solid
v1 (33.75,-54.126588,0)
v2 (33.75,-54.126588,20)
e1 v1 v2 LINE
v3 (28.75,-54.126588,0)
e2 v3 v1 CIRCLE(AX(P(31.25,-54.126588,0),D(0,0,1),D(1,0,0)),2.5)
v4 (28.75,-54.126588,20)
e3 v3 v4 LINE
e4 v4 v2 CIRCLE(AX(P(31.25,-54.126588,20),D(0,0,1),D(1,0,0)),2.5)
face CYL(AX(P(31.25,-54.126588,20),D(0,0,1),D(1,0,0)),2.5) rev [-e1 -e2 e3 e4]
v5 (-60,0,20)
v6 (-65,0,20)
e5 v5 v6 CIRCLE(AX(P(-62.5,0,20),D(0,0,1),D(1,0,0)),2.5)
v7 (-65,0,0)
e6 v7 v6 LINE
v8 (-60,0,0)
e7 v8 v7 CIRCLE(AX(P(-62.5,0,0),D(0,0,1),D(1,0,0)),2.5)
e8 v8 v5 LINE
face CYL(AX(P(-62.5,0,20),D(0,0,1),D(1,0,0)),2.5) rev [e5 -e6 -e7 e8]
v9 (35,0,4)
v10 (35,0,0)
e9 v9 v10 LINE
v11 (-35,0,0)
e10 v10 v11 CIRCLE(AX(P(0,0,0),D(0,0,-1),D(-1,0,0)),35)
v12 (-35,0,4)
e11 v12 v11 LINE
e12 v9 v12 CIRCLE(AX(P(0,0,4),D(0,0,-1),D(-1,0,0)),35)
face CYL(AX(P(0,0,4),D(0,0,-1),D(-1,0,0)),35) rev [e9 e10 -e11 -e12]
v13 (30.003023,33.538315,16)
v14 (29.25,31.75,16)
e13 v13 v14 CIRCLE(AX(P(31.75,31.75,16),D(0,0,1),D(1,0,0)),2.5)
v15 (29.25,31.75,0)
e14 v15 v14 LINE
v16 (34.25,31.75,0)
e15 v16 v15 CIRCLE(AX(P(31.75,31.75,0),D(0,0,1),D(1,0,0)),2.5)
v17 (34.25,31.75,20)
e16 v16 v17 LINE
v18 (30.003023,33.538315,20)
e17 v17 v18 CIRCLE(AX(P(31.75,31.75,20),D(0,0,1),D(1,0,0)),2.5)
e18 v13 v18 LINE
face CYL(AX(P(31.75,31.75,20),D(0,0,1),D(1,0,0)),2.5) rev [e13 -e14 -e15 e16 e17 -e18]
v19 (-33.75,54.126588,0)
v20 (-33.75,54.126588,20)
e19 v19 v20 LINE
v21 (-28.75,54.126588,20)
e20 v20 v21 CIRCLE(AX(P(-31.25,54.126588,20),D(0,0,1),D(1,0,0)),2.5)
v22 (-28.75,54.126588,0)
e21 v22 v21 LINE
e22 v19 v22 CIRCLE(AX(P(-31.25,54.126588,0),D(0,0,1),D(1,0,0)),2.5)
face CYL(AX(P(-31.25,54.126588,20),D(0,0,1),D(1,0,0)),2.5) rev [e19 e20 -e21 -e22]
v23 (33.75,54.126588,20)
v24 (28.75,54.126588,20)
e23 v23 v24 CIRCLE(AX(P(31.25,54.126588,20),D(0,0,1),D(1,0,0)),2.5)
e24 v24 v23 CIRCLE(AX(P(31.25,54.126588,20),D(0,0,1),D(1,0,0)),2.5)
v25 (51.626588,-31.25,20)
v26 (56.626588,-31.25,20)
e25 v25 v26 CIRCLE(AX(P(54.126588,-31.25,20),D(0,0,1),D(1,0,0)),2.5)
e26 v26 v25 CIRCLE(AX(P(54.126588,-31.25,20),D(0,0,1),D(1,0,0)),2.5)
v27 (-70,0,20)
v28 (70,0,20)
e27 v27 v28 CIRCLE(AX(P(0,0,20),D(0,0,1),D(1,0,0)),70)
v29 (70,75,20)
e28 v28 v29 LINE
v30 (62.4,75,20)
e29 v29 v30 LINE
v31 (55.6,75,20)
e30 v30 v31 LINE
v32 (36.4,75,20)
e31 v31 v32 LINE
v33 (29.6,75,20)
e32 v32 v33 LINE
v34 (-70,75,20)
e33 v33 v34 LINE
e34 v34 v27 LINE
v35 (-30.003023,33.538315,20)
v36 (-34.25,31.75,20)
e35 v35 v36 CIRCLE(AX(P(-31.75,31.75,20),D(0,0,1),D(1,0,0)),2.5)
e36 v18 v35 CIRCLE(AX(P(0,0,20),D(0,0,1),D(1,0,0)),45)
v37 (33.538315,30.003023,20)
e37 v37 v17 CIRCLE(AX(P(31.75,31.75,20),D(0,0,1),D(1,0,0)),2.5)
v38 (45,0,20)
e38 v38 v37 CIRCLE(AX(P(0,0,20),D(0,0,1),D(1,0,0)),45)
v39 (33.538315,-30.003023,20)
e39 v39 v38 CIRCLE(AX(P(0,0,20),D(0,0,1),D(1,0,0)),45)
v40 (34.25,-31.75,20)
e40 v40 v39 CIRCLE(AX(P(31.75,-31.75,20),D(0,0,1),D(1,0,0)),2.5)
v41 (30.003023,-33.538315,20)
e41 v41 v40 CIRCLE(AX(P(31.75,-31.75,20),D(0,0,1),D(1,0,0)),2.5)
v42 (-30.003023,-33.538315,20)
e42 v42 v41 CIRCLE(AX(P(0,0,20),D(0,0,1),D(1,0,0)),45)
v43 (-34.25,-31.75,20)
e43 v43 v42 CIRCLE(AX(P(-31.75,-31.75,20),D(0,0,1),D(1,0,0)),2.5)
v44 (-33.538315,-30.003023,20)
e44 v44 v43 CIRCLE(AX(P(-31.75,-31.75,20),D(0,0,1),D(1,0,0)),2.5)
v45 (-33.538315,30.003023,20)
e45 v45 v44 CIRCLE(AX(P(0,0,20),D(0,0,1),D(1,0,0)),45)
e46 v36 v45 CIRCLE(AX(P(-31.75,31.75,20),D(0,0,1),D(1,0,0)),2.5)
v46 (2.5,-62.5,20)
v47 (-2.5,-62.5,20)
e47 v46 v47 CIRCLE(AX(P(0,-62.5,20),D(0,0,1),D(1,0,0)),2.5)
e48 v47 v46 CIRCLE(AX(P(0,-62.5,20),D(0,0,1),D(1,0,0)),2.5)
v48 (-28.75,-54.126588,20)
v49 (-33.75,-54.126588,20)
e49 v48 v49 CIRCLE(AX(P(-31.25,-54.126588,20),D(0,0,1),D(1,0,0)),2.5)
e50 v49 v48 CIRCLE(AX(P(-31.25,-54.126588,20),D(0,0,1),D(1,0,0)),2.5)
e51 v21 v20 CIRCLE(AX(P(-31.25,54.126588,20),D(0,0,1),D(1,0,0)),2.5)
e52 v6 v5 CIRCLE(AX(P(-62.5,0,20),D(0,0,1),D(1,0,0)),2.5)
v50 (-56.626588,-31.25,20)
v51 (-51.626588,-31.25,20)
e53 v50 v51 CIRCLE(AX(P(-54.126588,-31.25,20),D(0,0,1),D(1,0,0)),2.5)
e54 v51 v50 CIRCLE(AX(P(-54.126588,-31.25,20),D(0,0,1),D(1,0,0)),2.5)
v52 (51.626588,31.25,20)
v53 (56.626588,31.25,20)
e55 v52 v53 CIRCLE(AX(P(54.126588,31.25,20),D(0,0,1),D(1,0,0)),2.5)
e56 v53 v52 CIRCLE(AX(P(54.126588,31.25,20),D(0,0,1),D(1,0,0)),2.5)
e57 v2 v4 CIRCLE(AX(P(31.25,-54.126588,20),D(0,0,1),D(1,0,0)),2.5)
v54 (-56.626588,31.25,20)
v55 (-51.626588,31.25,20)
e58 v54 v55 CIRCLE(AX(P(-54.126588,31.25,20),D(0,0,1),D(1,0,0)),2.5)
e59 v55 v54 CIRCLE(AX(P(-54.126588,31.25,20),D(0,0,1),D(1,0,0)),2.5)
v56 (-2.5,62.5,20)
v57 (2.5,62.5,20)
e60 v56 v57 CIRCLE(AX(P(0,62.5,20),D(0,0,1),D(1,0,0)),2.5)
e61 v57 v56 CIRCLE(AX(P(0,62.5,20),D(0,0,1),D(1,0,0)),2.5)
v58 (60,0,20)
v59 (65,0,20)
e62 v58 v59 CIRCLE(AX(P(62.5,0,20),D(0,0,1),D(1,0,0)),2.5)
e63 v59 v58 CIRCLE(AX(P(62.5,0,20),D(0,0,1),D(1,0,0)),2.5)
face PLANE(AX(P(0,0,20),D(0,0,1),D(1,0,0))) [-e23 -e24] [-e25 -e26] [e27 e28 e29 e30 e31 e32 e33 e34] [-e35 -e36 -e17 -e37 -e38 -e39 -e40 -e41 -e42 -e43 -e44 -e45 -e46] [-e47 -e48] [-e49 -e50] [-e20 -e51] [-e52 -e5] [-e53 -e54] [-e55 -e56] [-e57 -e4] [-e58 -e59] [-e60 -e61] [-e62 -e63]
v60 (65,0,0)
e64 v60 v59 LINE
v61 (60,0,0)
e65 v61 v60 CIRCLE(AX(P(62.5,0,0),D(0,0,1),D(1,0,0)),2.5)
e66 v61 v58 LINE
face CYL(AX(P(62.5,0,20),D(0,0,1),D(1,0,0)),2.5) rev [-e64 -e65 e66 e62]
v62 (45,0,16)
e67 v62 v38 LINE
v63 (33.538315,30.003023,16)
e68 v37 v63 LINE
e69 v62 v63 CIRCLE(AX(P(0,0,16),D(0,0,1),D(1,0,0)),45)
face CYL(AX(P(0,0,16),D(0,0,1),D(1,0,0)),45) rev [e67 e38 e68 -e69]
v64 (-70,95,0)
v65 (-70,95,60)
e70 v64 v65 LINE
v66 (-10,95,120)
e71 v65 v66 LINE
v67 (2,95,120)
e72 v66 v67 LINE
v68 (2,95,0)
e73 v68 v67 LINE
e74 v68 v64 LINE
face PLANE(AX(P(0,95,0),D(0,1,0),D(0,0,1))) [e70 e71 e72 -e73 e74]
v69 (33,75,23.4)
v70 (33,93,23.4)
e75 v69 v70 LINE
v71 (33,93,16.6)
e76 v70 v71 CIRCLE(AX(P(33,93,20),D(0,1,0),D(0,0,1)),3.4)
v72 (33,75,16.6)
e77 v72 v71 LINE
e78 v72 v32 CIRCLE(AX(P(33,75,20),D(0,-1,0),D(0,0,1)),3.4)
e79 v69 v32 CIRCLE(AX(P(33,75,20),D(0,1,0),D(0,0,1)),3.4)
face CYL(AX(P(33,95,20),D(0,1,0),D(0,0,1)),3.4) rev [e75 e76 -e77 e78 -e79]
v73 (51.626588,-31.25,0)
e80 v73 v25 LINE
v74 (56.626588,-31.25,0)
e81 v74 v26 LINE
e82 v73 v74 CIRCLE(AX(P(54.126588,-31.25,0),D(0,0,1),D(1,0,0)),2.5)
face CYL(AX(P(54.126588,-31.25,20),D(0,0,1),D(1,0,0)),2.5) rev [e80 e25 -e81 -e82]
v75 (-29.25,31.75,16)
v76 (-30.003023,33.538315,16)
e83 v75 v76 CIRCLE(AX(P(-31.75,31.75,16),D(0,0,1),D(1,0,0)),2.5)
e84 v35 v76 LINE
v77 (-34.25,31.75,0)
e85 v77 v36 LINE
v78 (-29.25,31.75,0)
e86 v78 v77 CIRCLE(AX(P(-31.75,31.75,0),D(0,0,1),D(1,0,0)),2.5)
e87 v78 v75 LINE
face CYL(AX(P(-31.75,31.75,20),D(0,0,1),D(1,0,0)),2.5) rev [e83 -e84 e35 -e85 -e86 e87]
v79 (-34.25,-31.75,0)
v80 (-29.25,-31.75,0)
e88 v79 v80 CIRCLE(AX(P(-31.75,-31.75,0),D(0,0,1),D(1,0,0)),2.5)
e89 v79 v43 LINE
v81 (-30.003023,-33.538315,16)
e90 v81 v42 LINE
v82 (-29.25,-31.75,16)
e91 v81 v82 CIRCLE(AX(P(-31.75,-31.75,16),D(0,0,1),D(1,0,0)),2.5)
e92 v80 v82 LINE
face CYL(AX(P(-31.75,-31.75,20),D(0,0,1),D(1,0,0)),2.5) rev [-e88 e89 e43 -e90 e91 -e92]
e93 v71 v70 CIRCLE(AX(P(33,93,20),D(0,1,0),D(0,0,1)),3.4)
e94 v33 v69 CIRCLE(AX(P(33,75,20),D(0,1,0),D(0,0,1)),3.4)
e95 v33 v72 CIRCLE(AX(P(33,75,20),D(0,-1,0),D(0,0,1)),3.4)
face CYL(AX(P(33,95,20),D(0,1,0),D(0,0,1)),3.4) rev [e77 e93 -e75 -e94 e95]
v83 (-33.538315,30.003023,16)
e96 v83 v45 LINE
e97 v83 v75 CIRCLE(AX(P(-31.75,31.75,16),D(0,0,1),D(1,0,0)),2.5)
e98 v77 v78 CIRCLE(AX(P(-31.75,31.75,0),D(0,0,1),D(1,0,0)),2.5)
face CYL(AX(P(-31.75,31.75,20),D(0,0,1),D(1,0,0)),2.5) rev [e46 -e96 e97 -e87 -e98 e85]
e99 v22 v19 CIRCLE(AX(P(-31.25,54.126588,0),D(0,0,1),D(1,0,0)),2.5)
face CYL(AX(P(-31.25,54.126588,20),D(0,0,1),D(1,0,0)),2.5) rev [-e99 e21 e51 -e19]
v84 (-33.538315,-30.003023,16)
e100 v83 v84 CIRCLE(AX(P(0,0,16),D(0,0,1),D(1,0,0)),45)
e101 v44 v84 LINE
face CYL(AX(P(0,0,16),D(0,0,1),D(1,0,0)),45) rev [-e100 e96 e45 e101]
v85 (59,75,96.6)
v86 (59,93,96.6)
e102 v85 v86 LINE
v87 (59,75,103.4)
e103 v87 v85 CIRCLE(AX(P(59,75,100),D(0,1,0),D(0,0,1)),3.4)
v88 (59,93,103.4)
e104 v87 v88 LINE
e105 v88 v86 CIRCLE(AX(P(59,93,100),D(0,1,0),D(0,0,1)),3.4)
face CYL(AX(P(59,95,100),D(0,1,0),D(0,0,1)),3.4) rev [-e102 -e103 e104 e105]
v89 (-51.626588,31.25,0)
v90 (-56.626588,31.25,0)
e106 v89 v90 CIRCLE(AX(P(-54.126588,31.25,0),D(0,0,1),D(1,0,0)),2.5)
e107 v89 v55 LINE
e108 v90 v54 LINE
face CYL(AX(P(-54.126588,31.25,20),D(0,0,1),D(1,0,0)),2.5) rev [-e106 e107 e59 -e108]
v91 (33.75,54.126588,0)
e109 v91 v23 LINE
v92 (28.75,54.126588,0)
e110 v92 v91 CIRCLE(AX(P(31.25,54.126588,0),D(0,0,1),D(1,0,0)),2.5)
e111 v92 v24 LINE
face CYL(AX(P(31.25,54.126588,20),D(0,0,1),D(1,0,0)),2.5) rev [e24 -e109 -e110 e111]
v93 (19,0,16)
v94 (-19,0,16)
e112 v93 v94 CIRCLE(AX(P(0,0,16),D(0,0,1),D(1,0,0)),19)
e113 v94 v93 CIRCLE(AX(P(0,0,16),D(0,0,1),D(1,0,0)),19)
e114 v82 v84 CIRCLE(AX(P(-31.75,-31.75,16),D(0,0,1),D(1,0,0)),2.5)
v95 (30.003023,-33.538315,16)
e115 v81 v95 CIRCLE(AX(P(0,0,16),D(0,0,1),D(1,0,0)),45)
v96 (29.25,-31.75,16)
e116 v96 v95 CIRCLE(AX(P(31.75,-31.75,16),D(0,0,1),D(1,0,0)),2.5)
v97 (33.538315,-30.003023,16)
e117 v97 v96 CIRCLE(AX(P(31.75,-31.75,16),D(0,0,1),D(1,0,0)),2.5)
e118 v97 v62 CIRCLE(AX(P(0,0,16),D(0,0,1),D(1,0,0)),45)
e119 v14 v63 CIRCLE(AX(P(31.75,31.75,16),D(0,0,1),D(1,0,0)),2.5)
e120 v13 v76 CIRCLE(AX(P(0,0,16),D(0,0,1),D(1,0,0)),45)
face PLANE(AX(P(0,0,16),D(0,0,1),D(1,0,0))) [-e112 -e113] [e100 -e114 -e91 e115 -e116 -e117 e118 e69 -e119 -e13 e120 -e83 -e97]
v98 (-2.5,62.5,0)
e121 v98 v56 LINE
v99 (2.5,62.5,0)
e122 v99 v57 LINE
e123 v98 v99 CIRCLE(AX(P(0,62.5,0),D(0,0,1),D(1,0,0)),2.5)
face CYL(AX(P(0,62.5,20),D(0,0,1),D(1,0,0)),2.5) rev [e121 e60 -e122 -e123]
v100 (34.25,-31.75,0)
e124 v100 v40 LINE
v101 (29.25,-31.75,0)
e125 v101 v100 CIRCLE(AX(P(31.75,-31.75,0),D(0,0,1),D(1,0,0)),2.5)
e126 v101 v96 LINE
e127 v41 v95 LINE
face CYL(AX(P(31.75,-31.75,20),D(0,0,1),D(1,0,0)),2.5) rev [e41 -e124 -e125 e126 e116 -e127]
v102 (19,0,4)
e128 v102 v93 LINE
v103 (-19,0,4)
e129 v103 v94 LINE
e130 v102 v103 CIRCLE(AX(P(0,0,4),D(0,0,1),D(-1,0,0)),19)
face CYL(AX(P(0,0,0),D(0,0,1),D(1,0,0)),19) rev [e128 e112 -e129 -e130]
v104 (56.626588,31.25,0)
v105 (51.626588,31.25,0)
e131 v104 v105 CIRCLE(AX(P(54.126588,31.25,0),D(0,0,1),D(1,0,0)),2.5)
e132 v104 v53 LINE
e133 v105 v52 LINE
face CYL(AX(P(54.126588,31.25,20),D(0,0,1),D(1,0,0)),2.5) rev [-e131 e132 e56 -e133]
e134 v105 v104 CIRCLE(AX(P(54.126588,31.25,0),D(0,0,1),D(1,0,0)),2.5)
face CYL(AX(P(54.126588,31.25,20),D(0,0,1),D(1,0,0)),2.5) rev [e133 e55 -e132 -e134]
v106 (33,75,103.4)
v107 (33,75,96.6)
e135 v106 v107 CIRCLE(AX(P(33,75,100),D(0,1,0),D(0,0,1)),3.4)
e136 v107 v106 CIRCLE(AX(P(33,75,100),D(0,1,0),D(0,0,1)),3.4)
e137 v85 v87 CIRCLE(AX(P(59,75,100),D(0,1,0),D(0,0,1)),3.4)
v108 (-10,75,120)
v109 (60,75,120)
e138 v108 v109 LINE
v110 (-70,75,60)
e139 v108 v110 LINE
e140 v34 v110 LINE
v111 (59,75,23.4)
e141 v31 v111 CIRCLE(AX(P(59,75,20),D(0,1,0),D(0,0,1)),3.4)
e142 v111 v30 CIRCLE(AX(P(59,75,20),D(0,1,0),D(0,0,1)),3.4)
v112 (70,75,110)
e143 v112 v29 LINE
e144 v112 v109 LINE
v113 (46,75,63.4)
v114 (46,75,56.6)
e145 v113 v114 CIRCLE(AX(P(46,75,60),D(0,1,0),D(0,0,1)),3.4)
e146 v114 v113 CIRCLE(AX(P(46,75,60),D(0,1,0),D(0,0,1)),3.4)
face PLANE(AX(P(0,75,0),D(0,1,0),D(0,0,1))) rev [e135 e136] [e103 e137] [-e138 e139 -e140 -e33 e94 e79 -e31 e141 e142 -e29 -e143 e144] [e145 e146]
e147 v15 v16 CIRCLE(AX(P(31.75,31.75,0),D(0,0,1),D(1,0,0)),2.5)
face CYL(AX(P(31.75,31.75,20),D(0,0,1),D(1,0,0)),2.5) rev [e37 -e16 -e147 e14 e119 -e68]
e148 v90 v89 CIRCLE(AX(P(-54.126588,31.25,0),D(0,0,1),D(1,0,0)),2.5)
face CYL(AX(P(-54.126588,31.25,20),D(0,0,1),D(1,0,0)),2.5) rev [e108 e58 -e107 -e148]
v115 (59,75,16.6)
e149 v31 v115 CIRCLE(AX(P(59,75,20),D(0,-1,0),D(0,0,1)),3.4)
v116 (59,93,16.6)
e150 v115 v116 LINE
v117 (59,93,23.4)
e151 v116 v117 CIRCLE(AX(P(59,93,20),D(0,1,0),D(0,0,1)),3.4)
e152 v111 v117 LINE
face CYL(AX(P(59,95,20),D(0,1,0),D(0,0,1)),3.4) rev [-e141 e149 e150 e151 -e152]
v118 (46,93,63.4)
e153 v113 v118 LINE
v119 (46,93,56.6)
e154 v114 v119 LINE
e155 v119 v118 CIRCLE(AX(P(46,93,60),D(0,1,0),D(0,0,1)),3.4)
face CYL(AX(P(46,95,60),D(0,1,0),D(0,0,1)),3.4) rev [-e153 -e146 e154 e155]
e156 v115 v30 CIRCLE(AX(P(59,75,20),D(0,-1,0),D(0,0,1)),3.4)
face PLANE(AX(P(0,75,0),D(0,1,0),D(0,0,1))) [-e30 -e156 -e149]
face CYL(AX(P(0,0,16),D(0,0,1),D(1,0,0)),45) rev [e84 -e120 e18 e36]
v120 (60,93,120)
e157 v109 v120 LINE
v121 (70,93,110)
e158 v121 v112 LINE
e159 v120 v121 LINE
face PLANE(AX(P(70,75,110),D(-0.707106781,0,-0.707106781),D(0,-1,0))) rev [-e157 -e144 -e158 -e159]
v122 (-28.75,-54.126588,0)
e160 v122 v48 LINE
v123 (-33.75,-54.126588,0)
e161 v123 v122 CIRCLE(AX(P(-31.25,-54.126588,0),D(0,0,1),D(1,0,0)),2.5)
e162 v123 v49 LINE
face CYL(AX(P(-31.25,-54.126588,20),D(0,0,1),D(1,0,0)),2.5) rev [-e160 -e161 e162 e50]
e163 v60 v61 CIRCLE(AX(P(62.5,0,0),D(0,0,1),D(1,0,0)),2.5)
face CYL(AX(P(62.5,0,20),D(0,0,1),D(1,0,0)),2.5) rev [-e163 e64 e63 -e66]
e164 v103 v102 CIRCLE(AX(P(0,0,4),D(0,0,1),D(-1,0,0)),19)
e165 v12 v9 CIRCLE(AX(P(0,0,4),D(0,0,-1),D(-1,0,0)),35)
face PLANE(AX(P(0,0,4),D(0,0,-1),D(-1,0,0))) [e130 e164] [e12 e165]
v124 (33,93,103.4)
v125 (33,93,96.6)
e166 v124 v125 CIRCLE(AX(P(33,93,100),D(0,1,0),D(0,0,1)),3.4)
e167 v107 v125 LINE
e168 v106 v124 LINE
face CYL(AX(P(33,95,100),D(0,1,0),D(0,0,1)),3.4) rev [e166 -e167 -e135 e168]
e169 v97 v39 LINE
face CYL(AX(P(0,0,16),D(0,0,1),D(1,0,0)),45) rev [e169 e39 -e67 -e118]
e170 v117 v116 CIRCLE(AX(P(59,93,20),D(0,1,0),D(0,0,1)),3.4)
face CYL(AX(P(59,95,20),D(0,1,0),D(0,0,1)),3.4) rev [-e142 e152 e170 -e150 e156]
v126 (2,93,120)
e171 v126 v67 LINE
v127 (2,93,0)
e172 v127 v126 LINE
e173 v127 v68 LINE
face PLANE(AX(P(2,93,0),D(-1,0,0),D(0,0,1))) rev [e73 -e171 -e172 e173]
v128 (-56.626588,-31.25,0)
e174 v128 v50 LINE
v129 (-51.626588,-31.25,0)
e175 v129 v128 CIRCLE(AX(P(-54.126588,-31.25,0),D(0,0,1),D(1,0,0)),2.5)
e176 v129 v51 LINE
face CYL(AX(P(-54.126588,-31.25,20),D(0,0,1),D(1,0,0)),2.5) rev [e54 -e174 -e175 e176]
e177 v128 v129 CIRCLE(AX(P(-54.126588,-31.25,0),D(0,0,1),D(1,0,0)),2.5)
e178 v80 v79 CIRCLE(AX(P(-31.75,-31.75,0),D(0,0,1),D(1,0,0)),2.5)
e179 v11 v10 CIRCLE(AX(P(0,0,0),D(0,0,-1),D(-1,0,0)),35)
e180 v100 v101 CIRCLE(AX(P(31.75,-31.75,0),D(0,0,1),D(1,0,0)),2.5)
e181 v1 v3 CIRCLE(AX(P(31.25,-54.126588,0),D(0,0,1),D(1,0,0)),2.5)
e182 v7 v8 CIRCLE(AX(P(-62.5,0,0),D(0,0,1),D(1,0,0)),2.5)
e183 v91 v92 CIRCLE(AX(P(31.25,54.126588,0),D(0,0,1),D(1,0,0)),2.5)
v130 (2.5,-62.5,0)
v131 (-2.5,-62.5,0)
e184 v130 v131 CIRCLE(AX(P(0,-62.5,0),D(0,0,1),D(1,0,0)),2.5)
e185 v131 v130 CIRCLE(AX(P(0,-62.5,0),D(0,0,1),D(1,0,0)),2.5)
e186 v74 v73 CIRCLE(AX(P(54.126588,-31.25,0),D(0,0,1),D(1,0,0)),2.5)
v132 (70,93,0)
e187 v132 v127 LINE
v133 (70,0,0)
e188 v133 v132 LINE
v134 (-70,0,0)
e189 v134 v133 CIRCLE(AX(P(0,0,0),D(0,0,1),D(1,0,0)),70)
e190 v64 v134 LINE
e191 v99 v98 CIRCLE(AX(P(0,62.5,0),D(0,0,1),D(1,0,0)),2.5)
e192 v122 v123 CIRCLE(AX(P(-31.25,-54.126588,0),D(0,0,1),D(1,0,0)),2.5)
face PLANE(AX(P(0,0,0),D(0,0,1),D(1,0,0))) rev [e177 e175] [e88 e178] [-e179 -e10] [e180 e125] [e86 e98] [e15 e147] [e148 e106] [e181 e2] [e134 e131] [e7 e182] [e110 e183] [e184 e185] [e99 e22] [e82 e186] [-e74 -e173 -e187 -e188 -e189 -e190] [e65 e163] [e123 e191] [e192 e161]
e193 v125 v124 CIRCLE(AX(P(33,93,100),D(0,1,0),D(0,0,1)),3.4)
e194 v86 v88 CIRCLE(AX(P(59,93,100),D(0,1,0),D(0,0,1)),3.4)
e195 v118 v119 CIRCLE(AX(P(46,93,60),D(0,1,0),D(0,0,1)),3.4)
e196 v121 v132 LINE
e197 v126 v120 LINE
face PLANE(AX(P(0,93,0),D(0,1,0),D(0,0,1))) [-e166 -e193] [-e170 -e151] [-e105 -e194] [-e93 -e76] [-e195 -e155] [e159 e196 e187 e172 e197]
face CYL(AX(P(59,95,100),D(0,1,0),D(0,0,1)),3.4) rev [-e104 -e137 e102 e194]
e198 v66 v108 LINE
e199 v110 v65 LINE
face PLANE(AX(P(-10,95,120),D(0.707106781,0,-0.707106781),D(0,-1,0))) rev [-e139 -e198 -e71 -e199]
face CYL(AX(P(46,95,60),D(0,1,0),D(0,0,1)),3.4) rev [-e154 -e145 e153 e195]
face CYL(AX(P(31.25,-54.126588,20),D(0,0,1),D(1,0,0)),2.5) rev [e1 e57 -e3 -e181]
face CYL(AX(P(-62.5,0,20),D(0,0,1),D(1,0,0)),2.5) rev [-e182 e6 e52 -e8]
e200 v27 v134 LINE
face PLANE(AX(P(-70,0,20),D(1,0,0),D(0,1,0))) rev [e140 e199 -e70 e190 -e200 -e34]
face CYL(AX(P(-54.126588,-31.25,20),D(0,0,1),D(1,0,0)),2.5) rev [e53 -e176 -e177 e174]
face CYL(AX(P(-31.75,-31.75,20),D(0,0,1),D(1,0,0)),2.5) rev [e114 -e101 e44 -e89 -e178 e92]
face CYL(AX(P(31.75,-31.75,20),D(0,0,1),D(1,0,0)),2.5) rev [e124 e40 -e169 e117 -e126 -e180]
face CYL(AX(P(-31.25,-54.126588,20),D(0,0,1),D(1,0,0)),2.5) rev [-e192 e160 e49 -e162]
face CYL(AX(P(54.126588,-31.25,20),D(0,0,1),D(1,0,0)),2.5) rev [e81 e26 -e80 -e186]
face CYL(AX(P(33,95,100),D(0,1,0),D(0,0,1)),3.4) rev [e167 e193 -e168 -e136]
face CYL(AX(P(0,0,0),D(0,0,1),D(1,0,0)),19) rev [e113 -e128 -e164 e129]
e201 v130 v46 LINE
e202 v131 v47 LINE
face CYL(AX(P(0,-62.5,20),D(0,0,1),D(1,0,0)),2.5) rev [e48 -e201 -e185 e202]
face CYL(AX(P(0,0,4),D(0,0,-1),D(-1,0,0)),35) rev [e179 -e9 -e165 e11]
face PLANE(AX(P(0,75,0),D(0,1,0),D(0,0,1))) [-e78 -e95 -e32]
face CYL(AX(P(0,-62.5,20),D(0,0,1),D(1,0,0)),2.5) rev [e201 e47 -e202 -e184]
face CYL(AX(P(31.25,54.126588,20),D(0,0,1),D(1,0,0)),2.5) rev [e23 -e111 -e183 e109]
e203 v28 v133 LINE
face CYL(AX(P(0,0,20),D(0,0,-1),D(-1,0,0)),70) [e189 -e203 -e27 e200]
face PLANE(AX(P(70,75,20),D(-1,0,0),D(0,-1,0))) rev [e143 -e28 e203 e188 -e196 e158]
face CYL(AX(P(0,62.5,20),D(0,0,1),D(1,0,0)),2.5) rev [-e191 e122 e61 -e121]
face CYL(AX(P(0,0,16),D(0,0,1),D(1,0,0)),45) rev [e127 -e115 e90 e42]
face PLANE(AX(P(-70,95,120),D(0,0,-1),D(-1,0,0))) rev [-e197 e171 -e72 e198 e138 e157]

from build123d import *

# Parameters (mm, degrees)
EXTRUDE_1_DEPTH        = 20
SKETCH_2_R             = 45
CUT_EXTRUDE_1_DEPTH    = 4
SKETCH_3_R             = 19
CUT_EXTRUDE_2_DEPTH    = 104.831594421
SKETCH_4_R             = 35
CUT_EXTRUDE_3_DEPTH    = 4
HOLE_WIZARD_M6_1_D     = 5
HOLE_WIZARD_M6_2_D     = 5
SKETCH_15_W            = 140
SKETCH_15_H            = 120
EXTRUDE_2_DEPTH        = 20
SKETCH_20_W            = 68
SKETCH_20_H            = 120
CUT_EXTRUDE_4_DEPTH    = 2
CHAMFER_1_SIZE         = 10
CHAMFER_2_SIZE         = 60
HOLE_WIZARD_M8_1_D     = 6.8
HOLE_WIZARD_M8_1_DEPTH = 20


with BuildPart() as part:
    # 草图1 → 凸台-拉伸1 (new body)
    with BuildSketch(Plane.XY):
        with BuildLine():
            Line((-70, 0), (-70, 75))
            Line((-70, 75), (70, 75))
            Line((70, 75), (70, 0))
            ThreePointArc((70, 0), (0, -70), (-70, 0))
        make_face()
    extrude(amount=EXTRUDE_1_DEPTH)

    # 草图2 → 切除-拉伸1 (cut)
    with BuildSketch(Plane.XY.offset(20)):
        Circle(SKETCH_2_R)
    extrude(amount=-CUT_EXTRUDE_1_DEPTH, mode=Mode.SUBTRACT)

    # 草图3 → 切除-拉伸2 (cut, through all)
    with BuildSketch(Plane.XY.offset(16)):
        Circle(SKETCH_3_R)
    extrude(amount=-CUT_EXTRUDE_2_DEPTH, mode=Mode.SUBTRACT)

    # 草图4 → 切除-拉伸3 (cut)
    with BuildSketch(Plane(origin=(0, 0, 0), x_dir=(-1, 0, 0), z_dir=(0, 0, -1))):
        Circle(SKETCH_4_R)
    extrude(amount=-CUT_EXTRUDE_3_DEPTH, mode=Mode.SUBTRACT)

    # M6 螺纹孔1 (through all)
    with Locations(Plane.XY.offset(20)):
        with Locations((0, 62.5), (31.25, 54.126587737), (54.126587737, 31.25), (62.5, 0), (54.126587737, -31.25), (31.25, -54.126587737), (0, -62.5), (-31.25, -54.126587737), (-54.126587737, -31.25), (-62.5, 0), (-54.126587737, 31.25), (-31.25, 54.126587737)):
            Hole(HOLE_WIZARD_M6_1_D / 2)

    # M6 螺纹孔2 (through all)
    with Locations(Plane.XY.offset(20)):
        with Locations((0, 0), (31.75, 31.75), (-31.75, -31.75), (-31.75, 31.75), (31.75, -31.75)):
            Hole(HOLE_WIZARD_M6_2_D / 2)

    # 草图15 → 凸台-拉伸2 (add)
    with BuildSketch(Plane(origin=(0, 75, 0), x_dir=(1, 0, 0), z_dir=(0, 1, 0))):
        with Locations((0, -60)):
            Rectangle(SKETCH_15_W, SKETCH_15_H)
    extrude(amount=EXTRUDE_2_DEPTH)

    # 草图20 → 切除-拉伸4 (cut)
    with BuildSketch(Plane(origin=(0, 95, 0), x_dir=(1, 0, 0), z_dir=(0, 1, 0))):
        with Locations((36, -60)):
            Rectangle(SKETCH_20_W, SKETCH_20_H)
    extrude(amount=-CUT_EXTRUDE_4_DEPTH, mode=Mode.SUBTRACT)

    # 倒角1
    chamfer_1_edges = [part.edges().sort_by_distance(p)[0] for p in [
        (70, 84, 120),
    ]]
    chamfer(chamfer_1_edges, length=CHAMFER_1_SIZE)

    # 倒角2
    chamfer_2_edges = [part.edges().sort_by_distance(p)[0] for p in [
        (-70, 85, 120),
    ]]
    chamfer(chamfer_2_edges, length=CHAMFER_2_SIZE)

    # M8 螺纹孔1
    with Locations(Plane(origin=(0, 95, 0), x_dir=(1, 0, 0), z_dir=(0, 1, 0))):
        with Locations((33, -20), (59, -20), (46, -60), (33, -100), (59, -100)):
            Hole(HOLE_WIZARD_M8_1_D / 2, depth=HOLE_WIZARD_M8_1_DEPTH)


solid = part.part
